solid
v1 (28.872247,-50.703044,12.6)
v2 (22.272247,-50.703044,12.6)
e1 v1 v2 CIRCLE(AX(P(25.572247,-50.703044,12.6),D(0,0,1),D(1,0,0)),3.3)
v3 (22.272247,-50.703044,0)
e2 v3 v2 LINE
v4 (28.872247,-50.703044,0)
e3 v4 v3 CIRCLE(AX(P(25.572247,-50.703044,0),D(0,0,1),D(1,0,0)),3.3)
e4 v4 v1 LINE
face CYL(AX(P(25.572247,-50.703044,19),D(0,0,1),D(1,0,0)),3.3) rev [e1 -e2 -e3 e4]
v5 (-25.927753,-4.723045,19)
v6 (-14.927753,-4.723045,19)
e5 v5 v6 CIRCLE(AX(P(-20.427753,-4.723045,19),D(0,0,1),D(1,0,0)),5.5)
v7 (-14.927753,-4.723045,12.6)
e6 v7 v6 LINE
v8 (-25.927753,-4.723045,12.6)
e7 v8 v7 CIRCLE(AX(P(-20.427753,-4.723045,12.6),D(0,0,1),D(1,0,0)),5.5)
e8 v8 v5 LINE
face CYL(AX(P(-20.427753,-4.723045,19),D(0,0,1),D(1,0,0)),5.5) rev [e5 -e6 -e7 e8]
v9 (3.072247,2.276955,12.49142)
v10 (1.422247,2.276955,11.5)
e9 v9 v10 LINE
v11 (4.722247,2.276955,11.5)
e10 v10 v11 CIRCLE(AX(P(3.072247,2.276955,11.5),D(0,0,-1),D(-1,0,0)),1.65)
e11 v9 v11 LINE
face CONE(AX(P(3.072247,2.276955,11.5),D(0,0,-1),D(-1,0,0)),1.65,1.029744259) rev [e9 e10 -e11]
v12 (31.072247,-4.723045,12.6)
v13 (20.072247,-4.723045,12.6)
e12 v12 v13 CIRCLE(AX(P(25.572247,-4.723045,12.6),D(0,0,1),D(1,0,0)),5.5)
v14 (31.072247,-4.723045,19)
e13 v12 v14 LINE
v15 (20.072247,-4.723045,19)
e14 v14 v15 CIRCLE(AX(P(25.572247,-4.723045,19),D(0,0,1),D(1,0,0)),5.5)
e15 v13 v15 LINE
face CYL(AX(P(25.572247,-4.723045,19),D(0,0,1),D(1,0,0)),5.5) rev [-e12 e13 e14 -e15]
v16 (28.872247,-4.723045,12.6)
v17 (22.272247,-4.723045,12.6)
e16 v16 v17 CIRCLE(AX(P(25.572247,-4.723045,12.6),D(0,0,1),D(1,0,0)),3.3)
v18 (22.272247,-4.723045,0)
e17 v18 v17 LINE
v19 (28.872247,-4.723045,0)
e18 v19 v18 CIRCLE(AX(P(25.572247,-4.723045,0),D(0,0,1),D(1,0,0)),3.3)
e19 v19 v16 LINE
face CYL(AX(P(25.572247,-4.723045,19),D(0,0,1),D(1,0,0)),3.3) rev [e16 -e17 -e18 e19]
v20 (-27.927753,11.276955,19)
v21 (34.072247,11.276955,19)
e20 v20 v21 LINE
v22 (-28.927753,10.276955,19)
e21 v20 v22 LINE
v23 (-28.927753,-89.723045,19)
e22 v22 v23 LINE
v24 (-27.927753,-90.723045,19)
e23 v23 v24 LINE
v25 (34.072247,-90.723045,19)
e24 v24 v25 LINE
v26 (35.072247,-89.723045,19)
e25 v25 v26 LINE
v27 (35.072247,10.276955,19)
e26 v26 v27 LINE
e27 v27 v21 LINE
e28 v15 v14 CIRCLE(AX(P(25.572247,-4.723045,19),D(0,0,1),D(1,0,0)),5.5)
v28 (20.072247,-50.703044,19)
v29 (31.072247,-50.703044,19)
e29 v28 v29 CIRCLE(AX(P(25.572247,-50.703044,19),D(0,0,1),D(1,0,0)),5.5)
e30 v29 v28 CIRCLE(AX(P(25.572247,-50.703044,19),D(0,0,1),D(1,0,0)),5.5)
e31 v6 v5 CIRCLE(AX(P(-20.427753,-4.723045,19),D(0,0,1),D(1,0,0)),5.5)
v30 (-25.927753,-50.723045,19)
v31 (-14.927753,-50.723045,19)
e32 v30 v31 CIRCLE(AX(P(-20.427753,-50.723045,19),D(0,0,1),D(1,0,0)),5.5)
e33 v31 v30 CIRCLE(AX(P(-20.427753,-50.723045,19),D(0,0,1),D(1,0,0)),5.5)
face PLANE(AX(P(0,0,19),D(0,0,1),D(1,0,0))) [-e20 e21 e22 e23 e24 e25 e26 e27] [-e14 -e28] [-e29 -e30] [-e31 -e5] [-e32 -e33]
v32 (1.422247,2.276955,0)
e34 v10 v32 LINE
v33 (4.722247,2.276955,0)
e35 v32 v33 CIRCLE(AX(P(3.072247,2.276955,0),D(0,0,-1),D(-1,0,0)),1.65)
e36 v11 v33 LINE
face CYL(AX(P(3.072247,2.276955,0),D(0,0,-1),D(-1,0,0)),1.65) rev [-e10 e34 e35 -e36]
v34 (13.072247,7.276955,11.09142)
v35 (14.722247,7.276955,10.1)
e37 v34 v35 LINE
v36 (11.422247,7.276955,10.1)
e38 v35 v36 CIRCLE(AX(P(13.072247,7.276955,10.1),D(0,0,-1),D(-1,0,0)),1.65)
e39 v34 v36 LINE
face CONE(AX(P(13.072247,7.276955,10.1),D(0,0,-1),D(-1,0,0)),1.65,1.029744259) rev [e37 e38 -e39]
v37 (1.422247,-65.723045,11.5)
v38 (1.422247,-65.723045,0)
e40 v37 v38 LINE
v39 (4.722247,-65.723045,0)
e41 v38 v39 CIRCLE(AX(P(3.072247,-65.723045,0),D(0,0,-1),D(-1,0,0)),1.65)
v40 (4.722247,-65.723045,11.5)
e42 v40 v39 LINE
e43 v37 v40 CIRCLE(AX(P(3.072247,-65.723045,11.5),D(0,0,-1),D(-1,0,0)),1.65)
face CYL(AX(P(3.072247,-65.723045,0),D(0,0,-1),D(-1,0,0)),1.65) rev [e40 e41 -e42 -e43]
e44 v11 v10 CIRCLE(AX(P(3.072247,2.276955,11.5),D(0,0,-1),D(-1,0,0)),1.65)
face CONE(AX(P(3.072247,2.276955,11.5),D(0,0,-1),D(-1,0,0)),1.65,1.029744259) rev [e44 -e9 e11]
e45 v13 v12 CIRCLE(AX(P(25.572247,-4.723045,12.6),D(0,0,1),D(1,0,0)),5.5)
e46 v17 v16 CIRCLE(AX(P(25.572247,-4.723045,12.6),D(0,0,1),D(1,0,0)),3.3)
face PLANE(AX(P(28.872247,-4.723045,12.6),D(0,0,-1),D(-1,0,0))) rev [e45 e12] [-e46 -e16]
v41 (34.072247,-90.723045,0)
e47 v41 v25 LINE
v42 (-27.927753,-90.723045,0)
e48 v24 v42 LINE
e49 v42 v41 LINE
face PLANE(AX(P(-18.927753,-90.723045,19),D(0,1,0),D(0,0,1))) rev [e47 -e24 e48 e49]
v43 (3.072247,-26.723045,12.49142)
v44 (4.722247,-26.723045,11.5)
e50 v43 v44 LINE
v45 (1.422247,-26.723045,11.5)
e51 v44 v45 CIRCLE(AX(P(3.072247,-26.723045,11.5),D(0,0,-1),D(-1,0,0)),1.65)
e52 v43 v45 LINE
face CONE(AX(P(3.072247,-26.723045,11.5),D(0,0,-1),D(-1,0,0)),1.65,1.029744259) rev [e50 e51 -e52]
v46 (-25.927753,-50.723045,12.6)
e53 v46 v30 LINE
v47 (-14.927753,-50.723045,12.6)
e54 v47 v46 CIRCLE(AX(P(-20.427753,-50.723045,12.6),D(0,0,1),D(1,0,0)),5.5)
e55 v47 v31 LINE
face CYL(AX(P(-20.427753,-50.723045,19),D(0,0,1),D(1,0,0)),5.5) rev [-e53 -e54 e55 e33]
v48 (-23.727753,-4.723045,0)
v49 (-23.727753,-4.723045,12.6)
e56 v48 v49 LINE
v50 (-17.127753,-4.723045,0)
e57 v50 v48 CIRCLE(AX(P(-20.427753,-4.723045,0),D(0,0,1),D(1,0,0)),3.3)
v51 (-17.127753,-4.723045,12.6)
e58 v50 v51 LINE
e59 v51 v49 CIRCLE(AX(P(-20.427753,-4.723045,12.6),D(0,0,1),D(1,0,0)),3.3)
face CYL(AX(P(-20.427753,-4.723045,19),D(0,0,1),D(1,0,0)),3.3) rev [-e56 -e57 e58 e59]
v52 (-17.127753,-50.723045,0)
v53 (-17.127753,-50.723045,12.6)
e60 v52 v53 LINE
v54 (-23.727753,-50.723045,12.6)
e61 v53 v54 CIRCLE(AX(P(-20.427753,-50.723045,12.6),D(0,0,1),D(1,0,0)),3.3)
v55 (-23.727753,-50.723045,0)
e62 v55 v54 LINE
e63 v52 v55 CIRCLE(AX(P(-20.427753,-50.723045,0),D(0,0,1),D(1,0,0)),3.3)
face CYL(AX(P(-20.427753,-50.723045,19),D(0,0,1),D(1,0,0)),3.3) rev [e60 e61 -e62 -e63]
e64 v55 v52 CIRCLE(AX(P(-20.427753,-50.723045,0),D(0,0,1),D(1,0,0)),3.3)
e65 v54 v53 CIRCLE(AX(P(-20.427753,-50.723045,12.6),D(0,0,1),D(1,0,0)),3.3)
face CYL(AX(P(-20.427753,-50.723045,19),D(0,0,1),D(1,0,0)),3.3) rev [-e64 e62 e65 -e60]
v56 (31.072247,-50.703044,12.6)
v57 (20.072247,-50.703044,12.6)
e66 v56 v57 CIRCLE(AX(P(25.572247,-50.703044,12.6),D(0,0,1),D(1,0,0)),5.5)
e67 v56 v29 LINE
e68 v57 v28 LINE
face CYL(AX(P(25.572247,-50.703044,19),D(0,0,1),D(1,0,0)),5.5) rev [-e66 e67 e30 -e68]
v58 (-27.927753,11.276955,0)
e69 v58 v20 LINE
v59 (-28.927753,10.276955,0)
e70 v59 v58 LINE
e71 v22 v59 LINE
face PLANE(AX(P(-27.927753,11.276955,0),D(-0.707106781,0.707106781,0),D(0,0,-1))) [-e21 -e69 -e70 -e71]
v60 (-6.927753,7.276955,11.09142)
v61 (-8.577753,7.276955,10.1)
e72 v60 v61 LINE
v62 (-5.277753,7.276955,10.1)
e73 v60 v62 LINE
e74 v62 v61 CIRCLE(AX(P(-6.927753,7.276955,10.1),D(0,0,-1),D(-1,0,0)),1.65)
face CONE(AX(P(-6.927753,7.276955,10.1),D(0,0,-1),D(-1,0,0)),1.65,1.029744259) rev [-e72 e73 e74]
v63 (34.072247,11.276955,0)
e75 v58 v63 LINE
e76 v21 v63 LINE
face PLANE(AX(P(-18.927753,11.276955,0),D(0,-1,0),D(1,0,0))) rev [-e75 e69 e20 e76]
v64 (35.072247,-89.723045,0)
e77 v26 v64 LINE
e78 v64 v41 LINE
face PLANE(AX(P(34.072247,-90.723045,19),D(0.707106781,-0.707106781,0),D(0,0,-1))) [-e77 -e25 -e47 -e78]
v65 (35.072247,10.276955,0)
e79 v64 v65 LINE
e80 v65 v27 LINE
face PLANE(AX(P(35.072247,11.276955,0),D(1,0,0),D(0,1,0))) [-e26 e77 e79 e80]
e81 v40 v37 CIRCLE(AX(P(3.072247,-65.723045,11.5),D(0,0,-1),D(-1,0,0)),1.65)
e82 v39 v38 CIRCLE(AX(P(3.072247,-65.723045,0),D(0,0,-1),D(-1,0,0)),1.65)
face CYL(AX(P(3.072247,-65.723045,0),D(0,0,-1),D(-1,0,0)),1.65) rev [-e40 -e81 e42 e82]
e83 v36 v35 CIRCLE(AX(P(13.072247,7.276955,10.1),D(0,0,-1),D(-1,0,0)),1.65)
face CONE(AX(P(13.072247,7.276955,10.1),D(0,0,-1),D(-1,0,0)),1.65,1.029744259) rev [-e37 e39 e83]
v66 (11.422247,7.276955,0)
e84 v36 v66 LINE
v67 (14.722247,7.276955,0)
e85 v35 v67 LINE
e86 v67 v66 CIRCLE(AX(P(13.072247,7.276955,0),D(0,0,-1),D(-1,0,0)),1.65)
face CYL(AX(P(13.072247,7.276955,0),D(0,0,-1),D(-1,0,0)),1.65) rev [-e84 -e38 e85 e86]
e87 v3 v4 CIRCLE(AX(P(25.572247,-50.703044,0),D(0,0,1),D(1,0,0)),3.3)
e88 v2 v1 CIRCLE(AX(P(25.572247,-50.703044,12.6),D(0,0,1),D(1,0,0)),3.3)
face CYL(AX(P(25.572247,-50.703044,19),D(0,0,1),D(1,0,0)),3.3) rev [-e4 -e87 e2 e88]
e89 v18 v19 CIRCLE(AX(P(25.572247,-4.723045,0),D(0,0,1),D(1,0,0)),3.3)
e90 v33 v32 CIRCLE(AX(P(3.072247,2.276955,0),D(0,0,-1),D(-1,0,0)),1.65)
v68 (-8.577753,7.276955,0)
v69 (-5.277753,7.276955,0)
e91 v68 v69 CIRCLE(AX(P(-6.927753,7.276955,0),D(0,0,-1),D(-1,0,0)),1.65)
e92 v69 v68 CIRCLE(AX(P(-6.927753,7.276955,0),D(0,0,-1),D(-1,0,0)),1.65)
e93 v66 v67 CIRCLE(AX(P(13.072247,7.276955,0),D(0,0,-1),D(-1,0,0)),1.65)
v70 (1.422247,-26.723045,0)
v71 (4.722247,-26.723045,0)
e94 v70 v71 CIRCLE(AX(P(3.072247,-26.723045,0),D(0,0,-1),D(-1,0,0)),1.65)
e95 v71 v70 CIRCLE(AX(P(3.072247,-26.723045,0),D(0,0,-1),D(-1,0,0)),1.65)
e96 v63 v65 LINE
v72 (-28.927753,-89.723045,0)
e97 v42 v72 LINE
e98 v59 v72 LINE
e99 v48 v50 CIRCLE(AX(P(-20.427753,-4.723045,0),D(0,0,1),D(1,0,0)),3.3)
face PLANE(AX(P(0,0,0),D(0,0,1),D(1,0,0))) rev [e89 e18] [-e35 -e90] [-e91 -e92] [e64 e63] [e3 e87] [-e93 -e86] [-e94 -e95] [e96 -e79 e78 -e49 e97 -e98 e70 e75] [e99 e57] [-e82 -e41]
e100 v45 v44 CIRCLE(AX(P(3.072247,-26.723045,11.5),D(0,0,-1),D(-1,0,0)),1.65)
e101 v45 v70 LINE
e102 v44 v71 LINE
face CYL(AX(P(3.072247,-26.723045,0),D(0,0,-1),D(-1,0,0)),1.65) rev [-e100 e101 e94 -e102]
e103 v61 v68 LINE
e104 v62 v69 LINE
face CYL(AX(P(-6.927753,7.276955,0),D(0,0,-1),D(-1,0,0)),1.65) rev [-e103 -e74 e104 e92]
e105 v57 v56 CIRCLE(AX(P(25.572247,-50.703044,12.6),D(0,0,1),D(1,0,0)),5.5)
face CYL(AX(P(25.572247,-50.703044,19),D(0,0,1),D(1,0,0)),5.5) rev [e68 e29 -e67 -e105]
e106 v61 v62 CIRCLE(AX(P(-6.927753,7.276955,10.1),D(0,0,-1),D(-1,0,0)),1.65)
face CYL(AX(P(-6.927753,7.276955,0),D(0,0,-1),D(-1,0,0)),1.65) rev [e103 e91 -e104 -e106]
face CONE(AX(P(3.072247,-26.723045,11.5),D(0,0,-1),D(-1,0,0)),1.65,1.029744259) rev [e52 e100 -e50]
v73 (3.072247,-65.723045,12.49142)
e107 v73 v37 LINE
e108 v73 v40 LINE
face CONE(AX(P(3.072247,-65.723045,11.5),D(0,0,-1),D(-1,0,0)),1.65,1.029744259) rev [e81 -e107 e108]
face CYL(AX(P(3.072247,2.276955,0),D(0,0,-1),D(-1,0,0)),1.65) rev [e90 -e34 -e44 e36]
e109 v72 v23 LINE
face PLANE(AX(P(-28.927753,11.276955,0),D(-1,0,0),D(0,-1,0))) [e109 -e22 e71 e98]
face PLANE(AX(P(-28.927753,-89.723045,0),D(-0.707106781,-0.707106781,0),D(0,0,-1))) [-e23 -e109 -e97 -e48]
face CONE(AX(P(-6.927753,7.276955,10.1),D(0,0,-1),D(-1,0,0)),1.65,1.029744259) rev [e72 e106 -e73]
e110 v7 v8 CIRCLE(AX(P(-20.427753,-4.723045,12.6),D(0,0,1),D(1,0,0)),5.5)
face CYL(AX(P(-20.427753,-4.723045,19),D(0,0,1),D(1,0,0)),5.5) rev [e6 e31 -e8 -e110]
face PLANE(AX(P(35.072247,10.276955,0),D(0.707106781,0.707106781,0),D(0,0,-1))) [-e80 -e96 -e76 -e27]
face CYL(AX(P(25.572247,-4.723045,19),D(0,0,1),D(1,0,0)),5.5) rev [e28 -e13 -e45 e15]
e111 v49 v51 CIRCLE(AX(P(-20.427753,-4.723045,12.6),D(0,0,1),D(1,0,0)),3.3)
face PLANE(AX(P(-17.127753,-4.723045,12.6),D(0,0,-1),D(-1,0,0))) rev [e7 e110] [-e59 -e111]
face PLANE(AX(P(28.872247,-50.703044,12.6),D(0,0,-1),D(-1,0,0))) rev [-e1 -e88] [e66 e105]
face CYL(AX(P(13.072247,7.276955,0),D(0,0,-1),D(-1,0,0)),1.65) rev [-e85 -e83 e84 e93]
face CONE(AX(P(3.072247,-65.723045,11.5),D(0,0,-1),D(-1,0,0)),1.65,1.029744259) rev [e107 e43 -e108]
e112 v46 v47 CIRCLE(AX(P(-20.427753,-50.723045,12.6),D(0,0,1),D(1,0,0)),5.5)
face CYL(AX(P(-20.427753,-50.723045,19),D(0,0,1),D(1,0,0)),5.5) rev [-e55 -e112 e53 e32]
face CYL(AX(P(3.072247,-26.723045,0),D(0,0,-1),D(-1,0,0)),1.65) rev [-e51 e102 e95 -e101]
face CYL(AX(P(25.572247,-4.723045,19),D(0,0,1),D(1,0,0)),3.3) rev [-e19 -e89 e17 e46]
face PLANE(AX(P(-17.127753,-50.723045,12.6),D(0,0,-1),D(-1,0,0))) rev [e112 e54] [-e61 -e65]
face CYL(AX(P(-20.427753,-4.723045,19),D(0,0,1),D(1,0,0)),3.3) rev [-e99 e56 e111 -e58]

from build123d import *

# Parameters (mm, degrees)
SKETCH_15_W                  = 44
SKETCH_15_H                  = 120
EXTRUDE_1_DEPTH              = 19
HOLE_WIZARD_M4_2_D           = 3.3
HOLE_WIZARD_M4_2_DEPTH       = 11.5
HOLE_WIZARD_M4_2_TIP         = 0.991420021
SKETCH_21_W                  = 44
SKETCH_21_H                  = 18
CUT_EXTRUDE_4_DEPTH          = 19
HOLE_WIZARD_M4_1_D           = 3.3
HOLE_WIZARD_M4_1_DEPTH       = 10.1
HOLE_WIZARD_M4_1_TIP         = 0.991420021
CHAMFER_1_SIZE               = 1
SKETCH_24_W                  = 13.771291576
SKETCH_24_H                  = 102
SKETCH_24_W_2                = 13.032581782
EXTRUDE_2_DEPTH              = 19
HOLE_WIZARD_M6_1_D           = 6.6
HOLE_WIZARD_M6_1_CBORE_D     = 11
HOLE_WIZARD_M6_1_CBORE_DEPTH = 6.4
CHAMFER_2_SIZE               = 1


with BuildPart() as part:
    # 草图15 → 凸台-拉伸1 (new body)
    with BuildSketch(Plane.XY):
        with Locations((3.072247365, -30.72304468)):
            Rectangle(SKETCH_15_W, SKETCH_15_H)
    extrude(amount=EXTRUDE_1_DEPTH)

    # M4 螺纹孔2
    with Locations(Plane(origin=(0, 0, 0), x_dir=(-1, 0, 0), z_dir=(0, 0, -1))):
        with Locations((-3.072247365, 2.27695532), (-3.072247365, -26.72304468), (-3.072247365, -65.72304468)):
            Hole(HOLE_WIZARD_M4_2_D / 2, depth=HOLE_WIZARD_M4_2_DEPTH)
            with Locations((0, 0, -(HOLE_WIZARD_M4_2_DEPTH + HOLE_WIZARD_M4_2_TIP / 2))):  # 118° drill point
                Cone(0, HOLE_WIZARD_M4_2_D / 2, HOLE_WIZARD_M4_2_TIP, mode=Mode.SUBTRACT)

    # 草图21 → 切除-拉伸4 (cut)
    with BuildSketch(Plane.XY.offset(19)):
        with Locations((3.072247365, 20.27695532)):
            Rectangle(SKETCH_21_W, SKETCH_21_H)
    extrude(amount=-CUT_EXTRUDE_4_DEPTH, mode=Mode.SUBTRACT)

    # M4 螺纹孔1
    with Locations(Plane(origin=(0, 0, 0), x_dir=(-1, 0, 0), z_dir=(0, 0, -1))):
        with Locations((-13.072247365, 7.27695532), (6.927752635, 7.27695532)):
            Hole(HOLE_WIZARD_M4_1_D / 2, depth=HOLE_WIZARD_M4_1_DEPTH)
            with Locations((0, 0, -(HOLE_WIZARD_M4_1_DEPTH + HOLE_WIZARD_M4_1_TIP / 2))):  # 118° drill point
                Cone(0, HOLE_WIZARD_M4_1_D / 2, HOLE_WIZARD_M4_1_TIP, mode=Mode.SUBTRACT)

    # 倒角1
    chamfer_1_edges = [part.edges().sort_by_distance(p)[0] for p in [
        (-18.927752635, 11.27695532, 9.5),
        (25.072247365, 11.27695532, 9.5),
        (25.072247365, -90.72304468, 9.5),
        (-18.927752635, -90.72304468, 9.5),
    ]]
    chamfer(chamfer_1_edges, length=CHAMFER_1_SIZE)

    # 草图24 → 凸台-拉伸2 (add)
    with BuildSketch(Plane.XY.offset(19)):
        with Locations((-22.042106847, -39.72304468)):
            Rectangle(SKETCH_24_W, SKETCH_24_H)
        with Locations((28.555956474, -39.72304468)):
            Rectangle(SKETCH_24_W_2, SKETCH_24_H)
    extrude(amount=-EXTRUDE_2_DEPTH)

    # M6 六角凹头螺钉的柱形沉头孔1 (through all)
    with Locations(Plane.XY.offset(19)):
        with Locations((-20.427752635, -4.72304468), (25.572247365, -4.72304468), (25.572247365, -50.70304438), (-20.427752635, -50.72304468)):
            CounterBoreHole(HOLE_WIZARD_M6_1_D / 2, HOLE_WIZARD_M6_1_CBORE_D / 2, HOLE_WIZARD_M6_1_CBORE_DEPTH)

    # 倒角2
    chamfer_2_edges = [part.edges().sort_by_distance(p)[0] for p in [
        (35.072247365, -90.72304468, 9.5),
        (35.072247365, 11.27695532, 9.5),
        (-28.927752635, -90.72304468, 9.5),
        (-28.927752635, 11.27695532, 9.5),
    ]]
    chamfer(chamfer_2_edges, length=CHAMFER_2_SIZE)


solid = part.part
